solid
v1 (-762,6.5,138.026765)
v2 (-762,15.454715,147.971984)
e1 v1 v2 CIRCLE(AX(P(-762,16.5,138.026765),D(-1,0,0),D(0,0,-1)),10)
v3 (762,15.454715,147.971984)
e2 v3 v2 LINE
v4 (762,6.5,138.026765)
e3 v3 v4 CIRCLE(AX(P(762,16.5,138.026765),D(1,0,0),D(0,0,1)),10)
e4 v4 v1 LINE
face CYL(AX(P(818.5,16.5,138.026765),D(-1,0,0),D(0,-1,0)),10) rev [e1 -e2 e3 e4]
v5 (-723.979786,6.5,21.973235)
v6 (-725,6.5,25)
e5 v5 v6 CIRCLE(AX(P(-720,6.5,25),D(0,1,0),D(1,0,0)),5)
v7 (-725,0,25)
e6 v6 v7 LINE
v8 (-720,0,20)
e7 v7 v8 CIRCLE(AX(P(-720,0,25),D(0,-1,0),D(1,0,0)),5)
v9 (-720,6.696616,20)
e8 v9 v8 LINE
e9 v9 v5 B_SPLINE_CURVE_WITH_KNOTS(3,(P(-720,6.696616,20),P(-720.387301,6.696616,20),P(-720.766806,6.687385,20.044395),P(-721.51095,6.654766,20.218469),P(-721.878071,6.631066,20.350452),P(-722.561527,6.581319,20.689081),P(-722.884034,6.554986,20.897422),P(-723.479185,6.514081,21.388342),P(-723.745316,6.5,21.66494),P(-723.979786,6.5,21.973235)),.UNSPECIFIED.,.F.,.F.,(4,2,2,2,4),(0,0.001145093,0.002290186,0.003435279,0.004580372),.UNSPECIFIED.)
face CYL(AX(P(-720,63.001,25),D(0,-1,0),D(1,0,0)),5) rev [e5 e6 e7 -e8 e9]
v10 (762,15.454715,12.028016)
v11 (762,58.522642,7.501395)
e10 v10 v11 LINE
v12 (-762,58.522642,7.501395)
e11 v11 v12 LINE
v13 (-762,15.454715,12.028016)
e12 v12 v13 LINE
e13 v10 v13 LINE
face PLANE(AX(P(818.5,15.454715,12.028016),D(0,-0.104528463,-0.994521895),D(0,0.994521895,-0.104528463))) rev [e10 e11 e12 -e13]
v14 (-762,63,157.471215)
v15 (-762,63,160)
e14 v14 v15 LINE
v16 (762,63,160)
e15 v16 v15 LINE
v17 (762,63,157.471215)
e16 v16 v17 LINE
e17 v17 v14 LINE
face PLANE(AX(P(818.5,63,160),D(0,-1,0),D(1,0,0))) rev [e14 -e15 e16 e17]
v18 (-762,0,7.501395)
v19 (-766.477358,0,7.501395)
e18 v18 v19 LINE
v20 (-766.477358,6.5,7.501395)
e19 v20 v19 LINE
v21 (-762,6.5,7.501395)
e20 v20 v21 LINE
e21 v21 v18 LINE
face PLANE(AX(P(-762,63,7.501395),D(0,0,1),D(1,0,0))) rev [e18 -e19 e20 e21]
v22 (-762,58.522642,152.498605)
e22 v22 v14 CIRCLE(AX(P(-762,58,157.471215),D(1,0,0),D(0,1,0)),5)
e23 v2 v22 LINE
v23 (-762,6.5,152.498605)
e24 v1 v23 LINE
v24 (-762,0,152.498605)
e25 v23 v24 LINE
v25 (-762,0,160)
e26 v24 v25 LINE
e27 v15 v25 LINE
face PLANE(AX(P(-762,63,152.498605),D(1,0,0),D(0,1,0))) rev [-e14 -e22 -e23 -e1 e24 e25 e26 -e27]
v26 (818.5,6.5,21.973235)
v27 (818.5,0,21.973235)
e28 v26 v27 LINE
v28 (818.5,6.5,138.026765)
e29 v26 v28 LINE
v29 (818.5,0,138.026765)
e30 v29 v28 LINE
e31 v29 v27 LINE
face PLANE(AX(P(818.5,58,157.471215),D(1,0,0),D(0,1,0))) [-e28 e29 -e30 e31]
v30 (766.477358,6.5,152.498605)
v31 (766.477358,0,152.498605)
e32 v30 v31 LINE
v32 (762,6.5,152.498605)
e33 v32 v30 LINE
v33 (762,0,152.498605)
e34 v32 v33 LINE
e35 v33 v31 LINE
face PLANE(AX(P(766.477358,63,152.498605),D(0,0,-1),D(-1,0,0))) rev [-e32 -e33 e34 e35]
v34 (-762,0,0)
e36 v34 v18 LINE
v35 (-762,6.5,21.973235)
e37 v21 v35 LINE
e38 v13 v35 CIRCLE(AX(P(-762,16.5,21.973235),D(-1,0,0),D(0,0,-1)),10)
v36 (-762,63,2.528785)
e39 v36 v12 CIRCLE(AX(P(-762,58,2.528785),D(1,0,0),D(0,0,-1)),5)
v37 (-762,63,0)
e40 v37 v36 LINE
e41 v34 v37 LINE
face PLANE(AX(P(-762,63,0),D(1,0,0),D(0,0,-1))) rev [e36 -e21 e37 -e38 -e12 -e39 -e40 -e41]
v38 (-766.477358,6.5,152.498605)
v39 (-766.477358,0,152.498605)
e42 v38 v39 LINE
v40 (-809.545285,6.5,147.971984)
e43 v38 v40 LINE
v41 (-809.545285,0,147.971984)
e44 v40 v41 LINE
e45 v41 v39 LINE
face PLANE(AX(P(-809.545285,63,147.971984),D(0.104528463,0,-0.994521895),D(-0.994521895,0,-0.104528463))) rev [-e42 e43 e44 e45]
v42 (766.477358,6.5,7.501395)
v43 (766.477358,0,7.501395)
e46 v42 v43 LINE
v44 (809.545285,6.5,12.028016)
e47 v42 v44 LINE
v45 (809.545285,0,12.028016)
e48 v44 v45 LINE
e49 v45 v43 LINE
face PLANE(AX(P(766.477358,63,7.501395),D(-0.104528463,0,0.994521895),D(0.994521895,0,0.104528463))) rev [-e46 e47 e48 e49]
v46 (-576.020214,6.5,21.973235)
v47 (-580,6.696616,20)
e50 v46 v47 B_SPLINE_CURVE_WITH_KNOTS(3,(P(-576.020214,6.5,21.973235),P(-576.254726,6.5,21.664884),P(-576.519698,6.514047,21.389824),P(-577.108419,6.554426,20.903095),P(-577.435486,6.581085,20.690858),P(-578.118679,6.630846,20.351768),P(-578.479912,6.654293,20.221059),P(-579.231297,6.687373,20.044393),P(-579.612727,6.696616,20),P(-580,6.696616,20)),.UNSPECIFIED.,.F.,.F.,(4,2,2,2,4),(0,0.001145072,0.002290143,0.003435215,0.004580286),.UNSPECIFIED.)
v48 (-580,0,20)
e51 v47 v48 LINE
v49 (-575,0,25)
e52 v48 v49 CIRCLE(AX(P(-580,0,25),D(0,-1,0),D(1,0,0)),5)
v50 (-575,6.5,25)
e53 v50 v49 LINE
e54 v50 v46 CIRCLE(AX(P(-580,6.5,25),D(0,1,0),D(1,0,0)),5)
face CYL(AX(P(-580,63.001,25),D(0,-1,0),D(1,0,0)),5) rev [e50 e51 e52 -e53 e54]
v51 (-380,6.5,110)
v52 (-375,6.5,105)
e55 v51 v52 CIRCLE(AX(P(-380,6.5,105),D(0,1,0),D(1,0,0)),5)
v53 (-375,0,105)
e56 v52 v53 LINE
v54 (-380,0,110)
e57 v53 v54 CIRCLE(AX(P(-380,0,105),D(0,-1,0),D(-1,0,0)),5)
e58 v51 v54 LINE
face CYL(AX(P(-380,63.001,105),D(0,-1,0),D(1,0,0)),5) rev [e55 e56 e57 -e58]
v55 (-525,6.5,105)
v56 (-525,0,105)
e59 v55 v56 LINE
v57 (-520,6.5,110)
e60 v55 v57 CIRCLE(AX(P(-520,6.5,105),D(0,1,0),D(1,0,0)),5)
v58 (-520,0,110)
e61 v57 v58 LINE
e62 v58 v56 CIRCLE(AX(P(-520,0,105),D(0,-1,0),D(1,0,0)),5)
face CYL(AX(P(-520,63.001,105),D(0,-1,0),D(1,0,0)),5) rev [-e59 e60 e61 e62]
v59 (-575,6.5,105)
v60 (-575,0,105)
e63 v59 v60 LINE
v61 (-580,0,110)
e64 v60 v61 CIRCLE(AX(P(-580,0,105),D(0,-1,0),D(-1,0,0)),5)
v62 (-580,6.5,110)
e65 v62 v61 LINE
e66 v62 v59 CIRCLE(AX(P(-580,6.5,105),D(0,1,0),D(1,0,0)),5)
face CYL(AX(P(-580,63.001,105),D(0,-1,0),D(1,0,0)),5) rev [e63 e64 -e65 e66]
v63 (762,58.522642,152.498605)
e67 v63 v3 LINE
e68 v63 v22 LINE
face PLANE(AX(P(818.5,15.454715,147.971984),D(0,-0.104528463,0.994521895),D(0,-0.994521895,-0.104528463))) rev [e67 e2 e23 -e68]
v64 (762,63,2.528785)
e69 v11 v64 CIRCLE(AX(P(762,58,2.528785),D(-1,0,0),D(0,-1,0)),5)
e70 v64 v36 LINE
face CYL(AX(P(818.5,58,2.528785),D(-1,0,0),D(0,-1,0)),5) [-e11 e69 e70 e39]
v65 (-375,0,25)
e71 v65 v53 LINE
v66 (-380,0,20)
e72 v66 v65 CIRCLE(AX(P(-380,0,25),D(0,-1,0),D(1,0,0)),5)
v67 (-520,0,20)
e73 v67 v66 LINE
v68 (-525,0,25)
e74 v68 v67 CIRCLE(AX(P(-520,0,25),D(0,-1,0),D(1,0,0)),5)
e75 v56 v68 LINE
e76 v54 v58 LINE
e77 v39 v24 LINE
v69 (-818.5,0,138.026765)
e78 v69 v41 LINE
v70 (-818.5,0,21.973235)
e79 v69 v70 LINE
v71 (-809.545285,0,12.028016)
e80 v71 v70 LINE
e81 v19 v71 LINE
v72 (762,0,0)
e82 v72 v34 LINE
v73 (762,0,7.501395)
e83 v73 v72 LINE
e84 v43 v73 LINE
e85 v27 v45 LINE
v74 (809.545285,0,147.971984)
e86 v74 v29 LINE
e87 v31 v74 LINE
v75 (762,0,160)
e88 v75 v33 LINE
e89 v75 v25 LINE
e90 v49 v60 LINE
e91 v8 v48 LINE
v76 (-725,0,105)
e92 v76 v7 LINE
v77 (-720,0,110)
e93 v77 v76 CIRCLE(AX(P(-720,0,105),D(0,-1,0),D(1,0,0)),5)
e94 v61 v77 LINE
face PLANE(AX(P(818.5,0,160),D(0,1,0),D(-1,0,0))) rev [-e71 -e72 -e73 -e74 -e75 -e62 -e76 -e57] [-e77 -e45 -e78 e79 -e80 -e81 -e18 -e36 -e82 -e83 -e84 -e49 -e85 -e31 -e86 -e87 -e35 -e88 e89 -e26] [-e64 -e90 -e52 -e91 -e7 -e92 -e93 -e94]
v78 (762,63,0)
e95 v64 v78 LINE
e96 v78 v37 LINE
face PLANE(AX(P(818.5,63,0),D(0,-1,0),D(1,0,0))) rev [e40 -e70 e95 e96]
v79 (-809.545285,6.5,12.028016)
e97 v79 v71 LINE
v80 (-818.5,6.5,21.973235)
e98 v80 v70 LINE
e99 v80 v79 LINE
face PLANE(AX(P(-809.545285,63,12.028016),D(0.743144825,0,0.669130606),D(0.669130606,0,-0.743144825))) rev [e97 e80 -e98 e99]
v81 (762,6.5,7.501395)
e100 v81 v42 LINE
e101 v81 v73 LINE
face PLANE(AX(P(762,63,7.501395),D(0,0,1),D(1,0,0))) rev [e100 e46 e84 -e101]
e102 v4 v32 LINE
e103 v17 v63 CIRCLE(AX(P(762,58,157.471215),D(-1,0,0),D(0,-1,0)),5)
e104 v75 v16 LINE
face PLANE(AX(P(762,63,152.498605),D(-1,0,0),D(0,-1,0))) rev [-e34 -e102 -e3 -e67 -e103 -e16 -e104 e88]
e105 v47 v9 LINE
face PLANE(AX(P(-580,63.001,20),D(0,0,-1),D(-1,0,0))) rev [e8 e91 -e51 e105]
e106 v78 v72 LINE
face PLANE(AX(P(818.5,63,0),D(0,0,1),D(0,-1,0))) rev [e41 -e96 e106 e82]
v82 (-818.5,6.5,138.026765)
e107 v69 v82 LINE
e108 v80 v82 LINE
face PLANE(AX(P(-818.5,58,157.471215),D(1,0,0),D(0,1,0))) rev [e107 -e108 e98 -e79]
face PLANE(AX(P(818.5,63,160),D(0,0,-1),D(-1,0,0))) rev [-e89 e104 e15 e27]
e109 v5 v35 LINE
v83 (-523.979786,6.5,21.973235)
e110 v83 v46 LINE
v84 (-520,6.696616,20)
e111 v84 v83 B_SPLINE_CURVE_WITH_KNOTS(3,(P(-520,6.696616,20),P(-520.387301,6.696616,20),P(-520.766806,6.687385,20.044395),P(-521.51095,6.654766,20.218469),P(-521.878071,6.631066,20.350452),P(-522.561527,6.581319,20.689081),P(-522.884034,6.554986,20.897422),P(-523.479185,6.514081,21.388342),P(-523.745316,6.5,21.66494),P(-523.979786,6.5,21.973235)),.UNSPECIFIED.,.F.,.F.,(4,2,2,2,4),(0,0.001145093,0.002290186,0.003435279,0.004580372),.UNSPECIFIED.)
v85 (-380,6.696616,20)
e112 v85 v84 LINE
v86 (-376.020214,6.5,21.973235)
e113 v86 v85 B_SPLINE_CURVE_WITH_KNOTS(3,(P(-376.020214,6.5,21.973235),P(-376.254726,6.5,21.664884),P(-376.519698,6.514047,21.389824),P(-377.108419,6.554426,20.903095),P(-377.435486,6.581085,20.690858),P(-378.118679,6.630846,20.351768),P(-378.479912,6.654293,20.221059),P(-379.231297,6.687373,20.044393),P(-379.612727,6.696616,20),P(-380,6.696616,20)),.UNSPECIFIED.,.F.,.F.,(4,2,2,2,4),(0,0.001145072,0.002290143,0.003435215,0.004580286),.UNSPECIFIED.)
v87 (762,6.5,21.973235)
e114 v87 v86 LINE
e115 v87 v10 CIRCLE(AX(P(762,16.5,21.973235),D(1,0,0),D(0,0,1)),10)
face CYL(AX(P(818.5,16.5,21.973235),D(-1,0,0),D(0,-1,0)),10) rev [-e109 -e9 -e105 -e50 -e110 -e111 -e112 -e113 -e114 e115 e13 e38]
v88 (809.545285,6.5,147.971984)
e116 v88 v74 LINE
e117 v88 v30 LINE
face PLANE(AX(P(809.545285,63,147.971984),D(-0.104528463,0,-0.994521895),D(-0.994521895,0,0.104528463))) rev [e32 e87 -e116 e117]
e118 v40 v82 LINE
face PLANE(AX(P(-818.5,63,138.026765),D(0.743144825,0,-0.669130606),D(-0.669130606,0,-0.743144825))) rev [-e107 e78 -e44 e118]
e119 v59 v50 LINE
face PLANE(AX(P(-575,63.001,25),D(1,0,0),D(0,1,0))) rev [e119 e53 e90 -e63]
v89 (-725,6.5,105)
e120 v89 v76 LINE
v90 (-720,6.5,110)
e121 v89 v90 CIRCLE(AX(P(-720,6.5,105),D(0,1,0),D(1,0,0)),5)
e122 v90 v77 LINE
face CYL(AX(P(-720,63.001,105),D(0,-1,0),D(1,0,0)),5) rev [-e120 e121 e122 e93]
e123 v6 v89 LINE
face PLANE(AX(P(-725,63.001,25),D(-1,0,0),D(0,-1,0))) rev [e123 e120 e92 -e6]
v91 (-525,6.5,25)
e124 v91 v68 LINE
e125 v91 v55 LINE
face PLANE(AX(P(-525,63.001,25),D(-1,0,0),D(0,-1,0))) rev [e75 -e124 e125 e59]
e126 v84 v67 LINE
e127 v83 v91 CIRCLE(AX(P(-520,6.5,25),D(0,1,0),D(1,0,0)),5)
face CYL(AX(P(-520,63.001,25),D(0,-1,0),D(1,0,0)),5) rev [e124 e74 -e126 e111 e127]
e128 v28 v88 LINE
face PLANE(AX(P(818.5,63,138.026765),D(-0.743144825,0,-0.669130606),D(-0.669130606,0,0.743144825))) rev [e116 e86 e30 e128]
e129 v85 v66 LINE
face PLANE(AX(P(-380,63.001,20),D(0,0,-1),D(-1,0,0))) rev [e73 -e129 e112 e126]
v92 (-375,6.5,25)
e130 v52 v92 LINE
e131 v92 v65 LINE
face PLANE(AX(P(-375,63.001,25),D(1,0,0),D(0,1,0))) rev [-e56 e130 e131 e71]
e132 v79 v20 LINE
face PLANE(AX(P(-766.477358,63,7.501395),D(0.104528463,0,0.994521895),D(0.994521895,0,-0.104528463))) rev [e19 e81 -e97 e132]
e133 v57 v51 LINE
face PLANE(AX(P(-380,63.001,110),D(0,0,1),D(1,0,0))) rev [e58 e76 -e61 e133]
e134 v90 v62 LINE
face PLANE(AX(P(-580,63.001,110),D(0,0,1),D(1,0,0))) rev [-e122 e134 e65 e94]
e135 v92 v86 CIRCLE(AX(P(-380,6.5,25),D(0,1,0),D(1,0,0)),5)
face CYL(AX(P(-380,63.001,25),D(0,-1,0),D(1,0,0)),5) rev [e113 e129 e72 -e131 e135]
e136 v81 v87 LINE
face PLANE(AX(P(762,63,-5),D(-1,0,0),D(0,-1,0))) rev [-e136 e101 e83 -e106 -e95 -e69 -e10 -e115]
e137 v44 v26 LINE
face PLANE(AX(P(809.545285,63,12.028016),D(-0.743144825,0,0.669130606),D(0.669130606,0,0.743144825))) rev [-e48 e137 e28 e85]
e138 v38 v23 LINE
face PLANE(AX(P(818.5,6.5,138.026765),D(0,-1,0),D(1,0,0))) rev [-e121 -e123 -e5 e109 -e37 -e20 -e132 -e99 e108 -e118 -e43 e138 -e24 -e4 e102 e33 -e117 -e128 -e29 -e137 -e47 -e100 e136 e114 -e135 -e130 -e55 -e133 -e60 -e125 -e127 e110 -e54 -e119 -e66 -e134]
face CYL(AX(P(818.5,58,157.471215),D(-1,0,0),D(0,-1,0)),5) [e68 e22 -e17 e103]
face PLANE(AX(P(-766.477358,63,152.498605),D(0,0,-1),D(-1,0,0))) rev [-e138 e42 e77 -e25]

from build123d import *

# Parameters (mm, degrees)
GBT706_2008_16A_1_DEPTH = 1637
CUT_EXTRUDE_1_DEPTH     = 837.367891541
CUT_EXTRUDE_2_DEPTH     = 837.367891541
SKETCH_4_W              = 56.5
SKETCH_4_H              = 56.5
CUT_EXTRUDE_3_DEPTH     = 835.965313439
SKETCH_5_W              = 56.5
SKETCH_5_H              = 56.5
CUT_EXTRUDE_4_DEPTH     = 835.965313439
CUT_EXTRUDE_5_REACH     = 838.368


with BuildPart() as part:
    # Sketch12 → Gbt706-2008 热轧槽钢 16A(1) (new body)
    with BuildSketch(Plane.YZ.offset(-818.5)):
        with BuildLine():
            Line((63, 160), (0, 160))
            Line((0, 160), (0, 0))
            Line((0, 0), (63, 0))
            Line((63, 0), (63, 2.528785132))
            ThreePointArc((63, 2.528785132), (61.715724127, 5.874438164), (58.522642316, 7.501394609))
            Line((58.522642316, 7.501394609), (15.454715367, 12.028016136))
            ThreePointArc((15.454715367, 12.028016136), (9.068551745, 15.281929026), (6.5, 21.973235089))
            Line((6.5, 21.973235089), (6.5, 138.026764911))
            ThreePointArc((6.5, 138.026764911), (9.068551745, 144.718070974), (15.454715367, 147.971983864))
            Line((15.454715367, 147.971983864), (58.522642316, 152.498605391))
            ThreePointArc((58.522642316, 152.498605391), (61.715724127, 154.125561836), (63, 157.471214868))
            Line((63, 157.471214868), (63, 160))
        make_face()
    extrude(amount=GBT706_2008_16A_1_DEPTH)

    # 草图2 → 切除-拉伸1 (cut, through all)
    with BuildSketch(Plane.XZ):
        Polygon((762, -5), (762, 7.501394609), (766.477357684, 7.501394609), (809.545284633, 12.028016136), (818.5, 21.973235089), (818.5, 138.026764911), (809.545284633, 147.971983864), (766.477357684, 152.498605391), (762, 152.498605391), (762, 165), (828.5, 165), (828.5, -5), align=None)
    extrude(amount=-CUT_EXTRUDE_1_DEPTH, mode=Mode.SUBTRACT)

    # 草图3 → 切除-拉伸2 (cut, through all)
    with BuildSketch(Plane.XZ):
        Polygon((-762, 0), (-762, 7.501394609), (-766.477357684, 7.501394609), (-809.545284633, 12.028016136), (-818.5, 21.973235089), (-818.5, 138.026764911), (-809.545284633, 147.971983864), (-766.477357684, 152.498605391), (-762, 152.498605391), (-762, 165), (-838.5, 165), (-838.5, -5), (-762, -5), align=None)
    extrude(amount=-CUT_EXTRUDE_2_DEPTH, mode=Mode.SUBTRACT)

    # 草图4 → 切除-拉伸3 (cut, through all)
    with BuildSketch(Plane.XY.offset(152.498605391)):
        with Locations((790.25, 34.75)):
            Rectangle(SKETCH_4_W, SKETCH_4_H)
    extrude(amount=-CUT_EXTRUDE_3_DEPTH, mode=Mode.SUBTRACT)

    # 草图5 → 切除-拉伸4 (cut, through all)
    with BuildSketch(Plane.XY.offset(152.498605391)):
        with Locations((-790.25, 34.75)):
            Rectangle(SKETCH_5_W, SKETCH_5_H)
    extrude(amount=-CUT_EXTRUDE_4_DEPTH, mode=Mode.SUBTRACT)

    # 草图6 → 切除-拉伸5 (cut, up to next)
    with BuildSketch(Plane.XZ, mode=Mode.PRIVATE) as cut_extrude_5_sk1:
        with BuildLine():
            Line((-580, 20), (-720, 20))
            ThreePointArc((-720, 20), (-723.535533906, 21.464466094), (-725, 25))
            Line((-725, 25), (-725, 105))
            ThreePointArc((-725, 105), (-723.535533906, 108.535533906), (-720, 110))
            Line((-720, 110), (-580, 110))
            ThreePointArc((-580, 110), (-576.464466094, 108.535533906), (-575, 105))
            Line((-575, 105), (-575, 25))
            ThreePointArc((-575, 25), (-576.464466094, 21.464466094), (-580, 20))
        make_face()
    cut_extrude_5_tool1 = extrude(cut_extrude_5_sk1.sketch, amount=-CUT_EXTRUDE_5_REACH, mode=Mode.PRIVATE) & part.part
    # 草图6 → 切除-拉伸5 (cut, up to next)
    with BuildSketch(Plane.XZ, mode=Mode.PRIVATE) as cut_extrude_5_sk2:
        with BuildLine():
            Line((-375, 25), (-375, 105))
            ThreePointArc((-375, 105), (-376.464466094, 108.535533906), (-380, 110))
            Line((-380, 110), (-520, 110))
            ThreePointArc((-520, 110), (-523.535533906, 108.535533906), (-525, 105))
            Line((-525, 105), (-525, 25))
            ThreePointArc((-525, 25), (-523.535533906, 21.464466094), (-520, 20))
            Line((-520, 20), (-380, 20))
            ThreePointArc((-380, 20), (-376.464466094, 21.464466094), (-375, 25))
        make_face()
    cut_extrude_5_tool2 = extrude(cut_extrude_5_sk2.sketch, amount=-CUT_EXTRUDE_5_REACH, mode=Mode.PRIVATE) & part.part
    add(cut_extrude_5_tool1.solids().sort_by_distance((-650, 0, 65))[0], mode=Mode.SUBTRACT)
    add(cut_extrude_5_tool2.solids().sort_by_distance((-450, 0, 65))[0], mode=Mode.SUBTRACT)


solid = part.part
